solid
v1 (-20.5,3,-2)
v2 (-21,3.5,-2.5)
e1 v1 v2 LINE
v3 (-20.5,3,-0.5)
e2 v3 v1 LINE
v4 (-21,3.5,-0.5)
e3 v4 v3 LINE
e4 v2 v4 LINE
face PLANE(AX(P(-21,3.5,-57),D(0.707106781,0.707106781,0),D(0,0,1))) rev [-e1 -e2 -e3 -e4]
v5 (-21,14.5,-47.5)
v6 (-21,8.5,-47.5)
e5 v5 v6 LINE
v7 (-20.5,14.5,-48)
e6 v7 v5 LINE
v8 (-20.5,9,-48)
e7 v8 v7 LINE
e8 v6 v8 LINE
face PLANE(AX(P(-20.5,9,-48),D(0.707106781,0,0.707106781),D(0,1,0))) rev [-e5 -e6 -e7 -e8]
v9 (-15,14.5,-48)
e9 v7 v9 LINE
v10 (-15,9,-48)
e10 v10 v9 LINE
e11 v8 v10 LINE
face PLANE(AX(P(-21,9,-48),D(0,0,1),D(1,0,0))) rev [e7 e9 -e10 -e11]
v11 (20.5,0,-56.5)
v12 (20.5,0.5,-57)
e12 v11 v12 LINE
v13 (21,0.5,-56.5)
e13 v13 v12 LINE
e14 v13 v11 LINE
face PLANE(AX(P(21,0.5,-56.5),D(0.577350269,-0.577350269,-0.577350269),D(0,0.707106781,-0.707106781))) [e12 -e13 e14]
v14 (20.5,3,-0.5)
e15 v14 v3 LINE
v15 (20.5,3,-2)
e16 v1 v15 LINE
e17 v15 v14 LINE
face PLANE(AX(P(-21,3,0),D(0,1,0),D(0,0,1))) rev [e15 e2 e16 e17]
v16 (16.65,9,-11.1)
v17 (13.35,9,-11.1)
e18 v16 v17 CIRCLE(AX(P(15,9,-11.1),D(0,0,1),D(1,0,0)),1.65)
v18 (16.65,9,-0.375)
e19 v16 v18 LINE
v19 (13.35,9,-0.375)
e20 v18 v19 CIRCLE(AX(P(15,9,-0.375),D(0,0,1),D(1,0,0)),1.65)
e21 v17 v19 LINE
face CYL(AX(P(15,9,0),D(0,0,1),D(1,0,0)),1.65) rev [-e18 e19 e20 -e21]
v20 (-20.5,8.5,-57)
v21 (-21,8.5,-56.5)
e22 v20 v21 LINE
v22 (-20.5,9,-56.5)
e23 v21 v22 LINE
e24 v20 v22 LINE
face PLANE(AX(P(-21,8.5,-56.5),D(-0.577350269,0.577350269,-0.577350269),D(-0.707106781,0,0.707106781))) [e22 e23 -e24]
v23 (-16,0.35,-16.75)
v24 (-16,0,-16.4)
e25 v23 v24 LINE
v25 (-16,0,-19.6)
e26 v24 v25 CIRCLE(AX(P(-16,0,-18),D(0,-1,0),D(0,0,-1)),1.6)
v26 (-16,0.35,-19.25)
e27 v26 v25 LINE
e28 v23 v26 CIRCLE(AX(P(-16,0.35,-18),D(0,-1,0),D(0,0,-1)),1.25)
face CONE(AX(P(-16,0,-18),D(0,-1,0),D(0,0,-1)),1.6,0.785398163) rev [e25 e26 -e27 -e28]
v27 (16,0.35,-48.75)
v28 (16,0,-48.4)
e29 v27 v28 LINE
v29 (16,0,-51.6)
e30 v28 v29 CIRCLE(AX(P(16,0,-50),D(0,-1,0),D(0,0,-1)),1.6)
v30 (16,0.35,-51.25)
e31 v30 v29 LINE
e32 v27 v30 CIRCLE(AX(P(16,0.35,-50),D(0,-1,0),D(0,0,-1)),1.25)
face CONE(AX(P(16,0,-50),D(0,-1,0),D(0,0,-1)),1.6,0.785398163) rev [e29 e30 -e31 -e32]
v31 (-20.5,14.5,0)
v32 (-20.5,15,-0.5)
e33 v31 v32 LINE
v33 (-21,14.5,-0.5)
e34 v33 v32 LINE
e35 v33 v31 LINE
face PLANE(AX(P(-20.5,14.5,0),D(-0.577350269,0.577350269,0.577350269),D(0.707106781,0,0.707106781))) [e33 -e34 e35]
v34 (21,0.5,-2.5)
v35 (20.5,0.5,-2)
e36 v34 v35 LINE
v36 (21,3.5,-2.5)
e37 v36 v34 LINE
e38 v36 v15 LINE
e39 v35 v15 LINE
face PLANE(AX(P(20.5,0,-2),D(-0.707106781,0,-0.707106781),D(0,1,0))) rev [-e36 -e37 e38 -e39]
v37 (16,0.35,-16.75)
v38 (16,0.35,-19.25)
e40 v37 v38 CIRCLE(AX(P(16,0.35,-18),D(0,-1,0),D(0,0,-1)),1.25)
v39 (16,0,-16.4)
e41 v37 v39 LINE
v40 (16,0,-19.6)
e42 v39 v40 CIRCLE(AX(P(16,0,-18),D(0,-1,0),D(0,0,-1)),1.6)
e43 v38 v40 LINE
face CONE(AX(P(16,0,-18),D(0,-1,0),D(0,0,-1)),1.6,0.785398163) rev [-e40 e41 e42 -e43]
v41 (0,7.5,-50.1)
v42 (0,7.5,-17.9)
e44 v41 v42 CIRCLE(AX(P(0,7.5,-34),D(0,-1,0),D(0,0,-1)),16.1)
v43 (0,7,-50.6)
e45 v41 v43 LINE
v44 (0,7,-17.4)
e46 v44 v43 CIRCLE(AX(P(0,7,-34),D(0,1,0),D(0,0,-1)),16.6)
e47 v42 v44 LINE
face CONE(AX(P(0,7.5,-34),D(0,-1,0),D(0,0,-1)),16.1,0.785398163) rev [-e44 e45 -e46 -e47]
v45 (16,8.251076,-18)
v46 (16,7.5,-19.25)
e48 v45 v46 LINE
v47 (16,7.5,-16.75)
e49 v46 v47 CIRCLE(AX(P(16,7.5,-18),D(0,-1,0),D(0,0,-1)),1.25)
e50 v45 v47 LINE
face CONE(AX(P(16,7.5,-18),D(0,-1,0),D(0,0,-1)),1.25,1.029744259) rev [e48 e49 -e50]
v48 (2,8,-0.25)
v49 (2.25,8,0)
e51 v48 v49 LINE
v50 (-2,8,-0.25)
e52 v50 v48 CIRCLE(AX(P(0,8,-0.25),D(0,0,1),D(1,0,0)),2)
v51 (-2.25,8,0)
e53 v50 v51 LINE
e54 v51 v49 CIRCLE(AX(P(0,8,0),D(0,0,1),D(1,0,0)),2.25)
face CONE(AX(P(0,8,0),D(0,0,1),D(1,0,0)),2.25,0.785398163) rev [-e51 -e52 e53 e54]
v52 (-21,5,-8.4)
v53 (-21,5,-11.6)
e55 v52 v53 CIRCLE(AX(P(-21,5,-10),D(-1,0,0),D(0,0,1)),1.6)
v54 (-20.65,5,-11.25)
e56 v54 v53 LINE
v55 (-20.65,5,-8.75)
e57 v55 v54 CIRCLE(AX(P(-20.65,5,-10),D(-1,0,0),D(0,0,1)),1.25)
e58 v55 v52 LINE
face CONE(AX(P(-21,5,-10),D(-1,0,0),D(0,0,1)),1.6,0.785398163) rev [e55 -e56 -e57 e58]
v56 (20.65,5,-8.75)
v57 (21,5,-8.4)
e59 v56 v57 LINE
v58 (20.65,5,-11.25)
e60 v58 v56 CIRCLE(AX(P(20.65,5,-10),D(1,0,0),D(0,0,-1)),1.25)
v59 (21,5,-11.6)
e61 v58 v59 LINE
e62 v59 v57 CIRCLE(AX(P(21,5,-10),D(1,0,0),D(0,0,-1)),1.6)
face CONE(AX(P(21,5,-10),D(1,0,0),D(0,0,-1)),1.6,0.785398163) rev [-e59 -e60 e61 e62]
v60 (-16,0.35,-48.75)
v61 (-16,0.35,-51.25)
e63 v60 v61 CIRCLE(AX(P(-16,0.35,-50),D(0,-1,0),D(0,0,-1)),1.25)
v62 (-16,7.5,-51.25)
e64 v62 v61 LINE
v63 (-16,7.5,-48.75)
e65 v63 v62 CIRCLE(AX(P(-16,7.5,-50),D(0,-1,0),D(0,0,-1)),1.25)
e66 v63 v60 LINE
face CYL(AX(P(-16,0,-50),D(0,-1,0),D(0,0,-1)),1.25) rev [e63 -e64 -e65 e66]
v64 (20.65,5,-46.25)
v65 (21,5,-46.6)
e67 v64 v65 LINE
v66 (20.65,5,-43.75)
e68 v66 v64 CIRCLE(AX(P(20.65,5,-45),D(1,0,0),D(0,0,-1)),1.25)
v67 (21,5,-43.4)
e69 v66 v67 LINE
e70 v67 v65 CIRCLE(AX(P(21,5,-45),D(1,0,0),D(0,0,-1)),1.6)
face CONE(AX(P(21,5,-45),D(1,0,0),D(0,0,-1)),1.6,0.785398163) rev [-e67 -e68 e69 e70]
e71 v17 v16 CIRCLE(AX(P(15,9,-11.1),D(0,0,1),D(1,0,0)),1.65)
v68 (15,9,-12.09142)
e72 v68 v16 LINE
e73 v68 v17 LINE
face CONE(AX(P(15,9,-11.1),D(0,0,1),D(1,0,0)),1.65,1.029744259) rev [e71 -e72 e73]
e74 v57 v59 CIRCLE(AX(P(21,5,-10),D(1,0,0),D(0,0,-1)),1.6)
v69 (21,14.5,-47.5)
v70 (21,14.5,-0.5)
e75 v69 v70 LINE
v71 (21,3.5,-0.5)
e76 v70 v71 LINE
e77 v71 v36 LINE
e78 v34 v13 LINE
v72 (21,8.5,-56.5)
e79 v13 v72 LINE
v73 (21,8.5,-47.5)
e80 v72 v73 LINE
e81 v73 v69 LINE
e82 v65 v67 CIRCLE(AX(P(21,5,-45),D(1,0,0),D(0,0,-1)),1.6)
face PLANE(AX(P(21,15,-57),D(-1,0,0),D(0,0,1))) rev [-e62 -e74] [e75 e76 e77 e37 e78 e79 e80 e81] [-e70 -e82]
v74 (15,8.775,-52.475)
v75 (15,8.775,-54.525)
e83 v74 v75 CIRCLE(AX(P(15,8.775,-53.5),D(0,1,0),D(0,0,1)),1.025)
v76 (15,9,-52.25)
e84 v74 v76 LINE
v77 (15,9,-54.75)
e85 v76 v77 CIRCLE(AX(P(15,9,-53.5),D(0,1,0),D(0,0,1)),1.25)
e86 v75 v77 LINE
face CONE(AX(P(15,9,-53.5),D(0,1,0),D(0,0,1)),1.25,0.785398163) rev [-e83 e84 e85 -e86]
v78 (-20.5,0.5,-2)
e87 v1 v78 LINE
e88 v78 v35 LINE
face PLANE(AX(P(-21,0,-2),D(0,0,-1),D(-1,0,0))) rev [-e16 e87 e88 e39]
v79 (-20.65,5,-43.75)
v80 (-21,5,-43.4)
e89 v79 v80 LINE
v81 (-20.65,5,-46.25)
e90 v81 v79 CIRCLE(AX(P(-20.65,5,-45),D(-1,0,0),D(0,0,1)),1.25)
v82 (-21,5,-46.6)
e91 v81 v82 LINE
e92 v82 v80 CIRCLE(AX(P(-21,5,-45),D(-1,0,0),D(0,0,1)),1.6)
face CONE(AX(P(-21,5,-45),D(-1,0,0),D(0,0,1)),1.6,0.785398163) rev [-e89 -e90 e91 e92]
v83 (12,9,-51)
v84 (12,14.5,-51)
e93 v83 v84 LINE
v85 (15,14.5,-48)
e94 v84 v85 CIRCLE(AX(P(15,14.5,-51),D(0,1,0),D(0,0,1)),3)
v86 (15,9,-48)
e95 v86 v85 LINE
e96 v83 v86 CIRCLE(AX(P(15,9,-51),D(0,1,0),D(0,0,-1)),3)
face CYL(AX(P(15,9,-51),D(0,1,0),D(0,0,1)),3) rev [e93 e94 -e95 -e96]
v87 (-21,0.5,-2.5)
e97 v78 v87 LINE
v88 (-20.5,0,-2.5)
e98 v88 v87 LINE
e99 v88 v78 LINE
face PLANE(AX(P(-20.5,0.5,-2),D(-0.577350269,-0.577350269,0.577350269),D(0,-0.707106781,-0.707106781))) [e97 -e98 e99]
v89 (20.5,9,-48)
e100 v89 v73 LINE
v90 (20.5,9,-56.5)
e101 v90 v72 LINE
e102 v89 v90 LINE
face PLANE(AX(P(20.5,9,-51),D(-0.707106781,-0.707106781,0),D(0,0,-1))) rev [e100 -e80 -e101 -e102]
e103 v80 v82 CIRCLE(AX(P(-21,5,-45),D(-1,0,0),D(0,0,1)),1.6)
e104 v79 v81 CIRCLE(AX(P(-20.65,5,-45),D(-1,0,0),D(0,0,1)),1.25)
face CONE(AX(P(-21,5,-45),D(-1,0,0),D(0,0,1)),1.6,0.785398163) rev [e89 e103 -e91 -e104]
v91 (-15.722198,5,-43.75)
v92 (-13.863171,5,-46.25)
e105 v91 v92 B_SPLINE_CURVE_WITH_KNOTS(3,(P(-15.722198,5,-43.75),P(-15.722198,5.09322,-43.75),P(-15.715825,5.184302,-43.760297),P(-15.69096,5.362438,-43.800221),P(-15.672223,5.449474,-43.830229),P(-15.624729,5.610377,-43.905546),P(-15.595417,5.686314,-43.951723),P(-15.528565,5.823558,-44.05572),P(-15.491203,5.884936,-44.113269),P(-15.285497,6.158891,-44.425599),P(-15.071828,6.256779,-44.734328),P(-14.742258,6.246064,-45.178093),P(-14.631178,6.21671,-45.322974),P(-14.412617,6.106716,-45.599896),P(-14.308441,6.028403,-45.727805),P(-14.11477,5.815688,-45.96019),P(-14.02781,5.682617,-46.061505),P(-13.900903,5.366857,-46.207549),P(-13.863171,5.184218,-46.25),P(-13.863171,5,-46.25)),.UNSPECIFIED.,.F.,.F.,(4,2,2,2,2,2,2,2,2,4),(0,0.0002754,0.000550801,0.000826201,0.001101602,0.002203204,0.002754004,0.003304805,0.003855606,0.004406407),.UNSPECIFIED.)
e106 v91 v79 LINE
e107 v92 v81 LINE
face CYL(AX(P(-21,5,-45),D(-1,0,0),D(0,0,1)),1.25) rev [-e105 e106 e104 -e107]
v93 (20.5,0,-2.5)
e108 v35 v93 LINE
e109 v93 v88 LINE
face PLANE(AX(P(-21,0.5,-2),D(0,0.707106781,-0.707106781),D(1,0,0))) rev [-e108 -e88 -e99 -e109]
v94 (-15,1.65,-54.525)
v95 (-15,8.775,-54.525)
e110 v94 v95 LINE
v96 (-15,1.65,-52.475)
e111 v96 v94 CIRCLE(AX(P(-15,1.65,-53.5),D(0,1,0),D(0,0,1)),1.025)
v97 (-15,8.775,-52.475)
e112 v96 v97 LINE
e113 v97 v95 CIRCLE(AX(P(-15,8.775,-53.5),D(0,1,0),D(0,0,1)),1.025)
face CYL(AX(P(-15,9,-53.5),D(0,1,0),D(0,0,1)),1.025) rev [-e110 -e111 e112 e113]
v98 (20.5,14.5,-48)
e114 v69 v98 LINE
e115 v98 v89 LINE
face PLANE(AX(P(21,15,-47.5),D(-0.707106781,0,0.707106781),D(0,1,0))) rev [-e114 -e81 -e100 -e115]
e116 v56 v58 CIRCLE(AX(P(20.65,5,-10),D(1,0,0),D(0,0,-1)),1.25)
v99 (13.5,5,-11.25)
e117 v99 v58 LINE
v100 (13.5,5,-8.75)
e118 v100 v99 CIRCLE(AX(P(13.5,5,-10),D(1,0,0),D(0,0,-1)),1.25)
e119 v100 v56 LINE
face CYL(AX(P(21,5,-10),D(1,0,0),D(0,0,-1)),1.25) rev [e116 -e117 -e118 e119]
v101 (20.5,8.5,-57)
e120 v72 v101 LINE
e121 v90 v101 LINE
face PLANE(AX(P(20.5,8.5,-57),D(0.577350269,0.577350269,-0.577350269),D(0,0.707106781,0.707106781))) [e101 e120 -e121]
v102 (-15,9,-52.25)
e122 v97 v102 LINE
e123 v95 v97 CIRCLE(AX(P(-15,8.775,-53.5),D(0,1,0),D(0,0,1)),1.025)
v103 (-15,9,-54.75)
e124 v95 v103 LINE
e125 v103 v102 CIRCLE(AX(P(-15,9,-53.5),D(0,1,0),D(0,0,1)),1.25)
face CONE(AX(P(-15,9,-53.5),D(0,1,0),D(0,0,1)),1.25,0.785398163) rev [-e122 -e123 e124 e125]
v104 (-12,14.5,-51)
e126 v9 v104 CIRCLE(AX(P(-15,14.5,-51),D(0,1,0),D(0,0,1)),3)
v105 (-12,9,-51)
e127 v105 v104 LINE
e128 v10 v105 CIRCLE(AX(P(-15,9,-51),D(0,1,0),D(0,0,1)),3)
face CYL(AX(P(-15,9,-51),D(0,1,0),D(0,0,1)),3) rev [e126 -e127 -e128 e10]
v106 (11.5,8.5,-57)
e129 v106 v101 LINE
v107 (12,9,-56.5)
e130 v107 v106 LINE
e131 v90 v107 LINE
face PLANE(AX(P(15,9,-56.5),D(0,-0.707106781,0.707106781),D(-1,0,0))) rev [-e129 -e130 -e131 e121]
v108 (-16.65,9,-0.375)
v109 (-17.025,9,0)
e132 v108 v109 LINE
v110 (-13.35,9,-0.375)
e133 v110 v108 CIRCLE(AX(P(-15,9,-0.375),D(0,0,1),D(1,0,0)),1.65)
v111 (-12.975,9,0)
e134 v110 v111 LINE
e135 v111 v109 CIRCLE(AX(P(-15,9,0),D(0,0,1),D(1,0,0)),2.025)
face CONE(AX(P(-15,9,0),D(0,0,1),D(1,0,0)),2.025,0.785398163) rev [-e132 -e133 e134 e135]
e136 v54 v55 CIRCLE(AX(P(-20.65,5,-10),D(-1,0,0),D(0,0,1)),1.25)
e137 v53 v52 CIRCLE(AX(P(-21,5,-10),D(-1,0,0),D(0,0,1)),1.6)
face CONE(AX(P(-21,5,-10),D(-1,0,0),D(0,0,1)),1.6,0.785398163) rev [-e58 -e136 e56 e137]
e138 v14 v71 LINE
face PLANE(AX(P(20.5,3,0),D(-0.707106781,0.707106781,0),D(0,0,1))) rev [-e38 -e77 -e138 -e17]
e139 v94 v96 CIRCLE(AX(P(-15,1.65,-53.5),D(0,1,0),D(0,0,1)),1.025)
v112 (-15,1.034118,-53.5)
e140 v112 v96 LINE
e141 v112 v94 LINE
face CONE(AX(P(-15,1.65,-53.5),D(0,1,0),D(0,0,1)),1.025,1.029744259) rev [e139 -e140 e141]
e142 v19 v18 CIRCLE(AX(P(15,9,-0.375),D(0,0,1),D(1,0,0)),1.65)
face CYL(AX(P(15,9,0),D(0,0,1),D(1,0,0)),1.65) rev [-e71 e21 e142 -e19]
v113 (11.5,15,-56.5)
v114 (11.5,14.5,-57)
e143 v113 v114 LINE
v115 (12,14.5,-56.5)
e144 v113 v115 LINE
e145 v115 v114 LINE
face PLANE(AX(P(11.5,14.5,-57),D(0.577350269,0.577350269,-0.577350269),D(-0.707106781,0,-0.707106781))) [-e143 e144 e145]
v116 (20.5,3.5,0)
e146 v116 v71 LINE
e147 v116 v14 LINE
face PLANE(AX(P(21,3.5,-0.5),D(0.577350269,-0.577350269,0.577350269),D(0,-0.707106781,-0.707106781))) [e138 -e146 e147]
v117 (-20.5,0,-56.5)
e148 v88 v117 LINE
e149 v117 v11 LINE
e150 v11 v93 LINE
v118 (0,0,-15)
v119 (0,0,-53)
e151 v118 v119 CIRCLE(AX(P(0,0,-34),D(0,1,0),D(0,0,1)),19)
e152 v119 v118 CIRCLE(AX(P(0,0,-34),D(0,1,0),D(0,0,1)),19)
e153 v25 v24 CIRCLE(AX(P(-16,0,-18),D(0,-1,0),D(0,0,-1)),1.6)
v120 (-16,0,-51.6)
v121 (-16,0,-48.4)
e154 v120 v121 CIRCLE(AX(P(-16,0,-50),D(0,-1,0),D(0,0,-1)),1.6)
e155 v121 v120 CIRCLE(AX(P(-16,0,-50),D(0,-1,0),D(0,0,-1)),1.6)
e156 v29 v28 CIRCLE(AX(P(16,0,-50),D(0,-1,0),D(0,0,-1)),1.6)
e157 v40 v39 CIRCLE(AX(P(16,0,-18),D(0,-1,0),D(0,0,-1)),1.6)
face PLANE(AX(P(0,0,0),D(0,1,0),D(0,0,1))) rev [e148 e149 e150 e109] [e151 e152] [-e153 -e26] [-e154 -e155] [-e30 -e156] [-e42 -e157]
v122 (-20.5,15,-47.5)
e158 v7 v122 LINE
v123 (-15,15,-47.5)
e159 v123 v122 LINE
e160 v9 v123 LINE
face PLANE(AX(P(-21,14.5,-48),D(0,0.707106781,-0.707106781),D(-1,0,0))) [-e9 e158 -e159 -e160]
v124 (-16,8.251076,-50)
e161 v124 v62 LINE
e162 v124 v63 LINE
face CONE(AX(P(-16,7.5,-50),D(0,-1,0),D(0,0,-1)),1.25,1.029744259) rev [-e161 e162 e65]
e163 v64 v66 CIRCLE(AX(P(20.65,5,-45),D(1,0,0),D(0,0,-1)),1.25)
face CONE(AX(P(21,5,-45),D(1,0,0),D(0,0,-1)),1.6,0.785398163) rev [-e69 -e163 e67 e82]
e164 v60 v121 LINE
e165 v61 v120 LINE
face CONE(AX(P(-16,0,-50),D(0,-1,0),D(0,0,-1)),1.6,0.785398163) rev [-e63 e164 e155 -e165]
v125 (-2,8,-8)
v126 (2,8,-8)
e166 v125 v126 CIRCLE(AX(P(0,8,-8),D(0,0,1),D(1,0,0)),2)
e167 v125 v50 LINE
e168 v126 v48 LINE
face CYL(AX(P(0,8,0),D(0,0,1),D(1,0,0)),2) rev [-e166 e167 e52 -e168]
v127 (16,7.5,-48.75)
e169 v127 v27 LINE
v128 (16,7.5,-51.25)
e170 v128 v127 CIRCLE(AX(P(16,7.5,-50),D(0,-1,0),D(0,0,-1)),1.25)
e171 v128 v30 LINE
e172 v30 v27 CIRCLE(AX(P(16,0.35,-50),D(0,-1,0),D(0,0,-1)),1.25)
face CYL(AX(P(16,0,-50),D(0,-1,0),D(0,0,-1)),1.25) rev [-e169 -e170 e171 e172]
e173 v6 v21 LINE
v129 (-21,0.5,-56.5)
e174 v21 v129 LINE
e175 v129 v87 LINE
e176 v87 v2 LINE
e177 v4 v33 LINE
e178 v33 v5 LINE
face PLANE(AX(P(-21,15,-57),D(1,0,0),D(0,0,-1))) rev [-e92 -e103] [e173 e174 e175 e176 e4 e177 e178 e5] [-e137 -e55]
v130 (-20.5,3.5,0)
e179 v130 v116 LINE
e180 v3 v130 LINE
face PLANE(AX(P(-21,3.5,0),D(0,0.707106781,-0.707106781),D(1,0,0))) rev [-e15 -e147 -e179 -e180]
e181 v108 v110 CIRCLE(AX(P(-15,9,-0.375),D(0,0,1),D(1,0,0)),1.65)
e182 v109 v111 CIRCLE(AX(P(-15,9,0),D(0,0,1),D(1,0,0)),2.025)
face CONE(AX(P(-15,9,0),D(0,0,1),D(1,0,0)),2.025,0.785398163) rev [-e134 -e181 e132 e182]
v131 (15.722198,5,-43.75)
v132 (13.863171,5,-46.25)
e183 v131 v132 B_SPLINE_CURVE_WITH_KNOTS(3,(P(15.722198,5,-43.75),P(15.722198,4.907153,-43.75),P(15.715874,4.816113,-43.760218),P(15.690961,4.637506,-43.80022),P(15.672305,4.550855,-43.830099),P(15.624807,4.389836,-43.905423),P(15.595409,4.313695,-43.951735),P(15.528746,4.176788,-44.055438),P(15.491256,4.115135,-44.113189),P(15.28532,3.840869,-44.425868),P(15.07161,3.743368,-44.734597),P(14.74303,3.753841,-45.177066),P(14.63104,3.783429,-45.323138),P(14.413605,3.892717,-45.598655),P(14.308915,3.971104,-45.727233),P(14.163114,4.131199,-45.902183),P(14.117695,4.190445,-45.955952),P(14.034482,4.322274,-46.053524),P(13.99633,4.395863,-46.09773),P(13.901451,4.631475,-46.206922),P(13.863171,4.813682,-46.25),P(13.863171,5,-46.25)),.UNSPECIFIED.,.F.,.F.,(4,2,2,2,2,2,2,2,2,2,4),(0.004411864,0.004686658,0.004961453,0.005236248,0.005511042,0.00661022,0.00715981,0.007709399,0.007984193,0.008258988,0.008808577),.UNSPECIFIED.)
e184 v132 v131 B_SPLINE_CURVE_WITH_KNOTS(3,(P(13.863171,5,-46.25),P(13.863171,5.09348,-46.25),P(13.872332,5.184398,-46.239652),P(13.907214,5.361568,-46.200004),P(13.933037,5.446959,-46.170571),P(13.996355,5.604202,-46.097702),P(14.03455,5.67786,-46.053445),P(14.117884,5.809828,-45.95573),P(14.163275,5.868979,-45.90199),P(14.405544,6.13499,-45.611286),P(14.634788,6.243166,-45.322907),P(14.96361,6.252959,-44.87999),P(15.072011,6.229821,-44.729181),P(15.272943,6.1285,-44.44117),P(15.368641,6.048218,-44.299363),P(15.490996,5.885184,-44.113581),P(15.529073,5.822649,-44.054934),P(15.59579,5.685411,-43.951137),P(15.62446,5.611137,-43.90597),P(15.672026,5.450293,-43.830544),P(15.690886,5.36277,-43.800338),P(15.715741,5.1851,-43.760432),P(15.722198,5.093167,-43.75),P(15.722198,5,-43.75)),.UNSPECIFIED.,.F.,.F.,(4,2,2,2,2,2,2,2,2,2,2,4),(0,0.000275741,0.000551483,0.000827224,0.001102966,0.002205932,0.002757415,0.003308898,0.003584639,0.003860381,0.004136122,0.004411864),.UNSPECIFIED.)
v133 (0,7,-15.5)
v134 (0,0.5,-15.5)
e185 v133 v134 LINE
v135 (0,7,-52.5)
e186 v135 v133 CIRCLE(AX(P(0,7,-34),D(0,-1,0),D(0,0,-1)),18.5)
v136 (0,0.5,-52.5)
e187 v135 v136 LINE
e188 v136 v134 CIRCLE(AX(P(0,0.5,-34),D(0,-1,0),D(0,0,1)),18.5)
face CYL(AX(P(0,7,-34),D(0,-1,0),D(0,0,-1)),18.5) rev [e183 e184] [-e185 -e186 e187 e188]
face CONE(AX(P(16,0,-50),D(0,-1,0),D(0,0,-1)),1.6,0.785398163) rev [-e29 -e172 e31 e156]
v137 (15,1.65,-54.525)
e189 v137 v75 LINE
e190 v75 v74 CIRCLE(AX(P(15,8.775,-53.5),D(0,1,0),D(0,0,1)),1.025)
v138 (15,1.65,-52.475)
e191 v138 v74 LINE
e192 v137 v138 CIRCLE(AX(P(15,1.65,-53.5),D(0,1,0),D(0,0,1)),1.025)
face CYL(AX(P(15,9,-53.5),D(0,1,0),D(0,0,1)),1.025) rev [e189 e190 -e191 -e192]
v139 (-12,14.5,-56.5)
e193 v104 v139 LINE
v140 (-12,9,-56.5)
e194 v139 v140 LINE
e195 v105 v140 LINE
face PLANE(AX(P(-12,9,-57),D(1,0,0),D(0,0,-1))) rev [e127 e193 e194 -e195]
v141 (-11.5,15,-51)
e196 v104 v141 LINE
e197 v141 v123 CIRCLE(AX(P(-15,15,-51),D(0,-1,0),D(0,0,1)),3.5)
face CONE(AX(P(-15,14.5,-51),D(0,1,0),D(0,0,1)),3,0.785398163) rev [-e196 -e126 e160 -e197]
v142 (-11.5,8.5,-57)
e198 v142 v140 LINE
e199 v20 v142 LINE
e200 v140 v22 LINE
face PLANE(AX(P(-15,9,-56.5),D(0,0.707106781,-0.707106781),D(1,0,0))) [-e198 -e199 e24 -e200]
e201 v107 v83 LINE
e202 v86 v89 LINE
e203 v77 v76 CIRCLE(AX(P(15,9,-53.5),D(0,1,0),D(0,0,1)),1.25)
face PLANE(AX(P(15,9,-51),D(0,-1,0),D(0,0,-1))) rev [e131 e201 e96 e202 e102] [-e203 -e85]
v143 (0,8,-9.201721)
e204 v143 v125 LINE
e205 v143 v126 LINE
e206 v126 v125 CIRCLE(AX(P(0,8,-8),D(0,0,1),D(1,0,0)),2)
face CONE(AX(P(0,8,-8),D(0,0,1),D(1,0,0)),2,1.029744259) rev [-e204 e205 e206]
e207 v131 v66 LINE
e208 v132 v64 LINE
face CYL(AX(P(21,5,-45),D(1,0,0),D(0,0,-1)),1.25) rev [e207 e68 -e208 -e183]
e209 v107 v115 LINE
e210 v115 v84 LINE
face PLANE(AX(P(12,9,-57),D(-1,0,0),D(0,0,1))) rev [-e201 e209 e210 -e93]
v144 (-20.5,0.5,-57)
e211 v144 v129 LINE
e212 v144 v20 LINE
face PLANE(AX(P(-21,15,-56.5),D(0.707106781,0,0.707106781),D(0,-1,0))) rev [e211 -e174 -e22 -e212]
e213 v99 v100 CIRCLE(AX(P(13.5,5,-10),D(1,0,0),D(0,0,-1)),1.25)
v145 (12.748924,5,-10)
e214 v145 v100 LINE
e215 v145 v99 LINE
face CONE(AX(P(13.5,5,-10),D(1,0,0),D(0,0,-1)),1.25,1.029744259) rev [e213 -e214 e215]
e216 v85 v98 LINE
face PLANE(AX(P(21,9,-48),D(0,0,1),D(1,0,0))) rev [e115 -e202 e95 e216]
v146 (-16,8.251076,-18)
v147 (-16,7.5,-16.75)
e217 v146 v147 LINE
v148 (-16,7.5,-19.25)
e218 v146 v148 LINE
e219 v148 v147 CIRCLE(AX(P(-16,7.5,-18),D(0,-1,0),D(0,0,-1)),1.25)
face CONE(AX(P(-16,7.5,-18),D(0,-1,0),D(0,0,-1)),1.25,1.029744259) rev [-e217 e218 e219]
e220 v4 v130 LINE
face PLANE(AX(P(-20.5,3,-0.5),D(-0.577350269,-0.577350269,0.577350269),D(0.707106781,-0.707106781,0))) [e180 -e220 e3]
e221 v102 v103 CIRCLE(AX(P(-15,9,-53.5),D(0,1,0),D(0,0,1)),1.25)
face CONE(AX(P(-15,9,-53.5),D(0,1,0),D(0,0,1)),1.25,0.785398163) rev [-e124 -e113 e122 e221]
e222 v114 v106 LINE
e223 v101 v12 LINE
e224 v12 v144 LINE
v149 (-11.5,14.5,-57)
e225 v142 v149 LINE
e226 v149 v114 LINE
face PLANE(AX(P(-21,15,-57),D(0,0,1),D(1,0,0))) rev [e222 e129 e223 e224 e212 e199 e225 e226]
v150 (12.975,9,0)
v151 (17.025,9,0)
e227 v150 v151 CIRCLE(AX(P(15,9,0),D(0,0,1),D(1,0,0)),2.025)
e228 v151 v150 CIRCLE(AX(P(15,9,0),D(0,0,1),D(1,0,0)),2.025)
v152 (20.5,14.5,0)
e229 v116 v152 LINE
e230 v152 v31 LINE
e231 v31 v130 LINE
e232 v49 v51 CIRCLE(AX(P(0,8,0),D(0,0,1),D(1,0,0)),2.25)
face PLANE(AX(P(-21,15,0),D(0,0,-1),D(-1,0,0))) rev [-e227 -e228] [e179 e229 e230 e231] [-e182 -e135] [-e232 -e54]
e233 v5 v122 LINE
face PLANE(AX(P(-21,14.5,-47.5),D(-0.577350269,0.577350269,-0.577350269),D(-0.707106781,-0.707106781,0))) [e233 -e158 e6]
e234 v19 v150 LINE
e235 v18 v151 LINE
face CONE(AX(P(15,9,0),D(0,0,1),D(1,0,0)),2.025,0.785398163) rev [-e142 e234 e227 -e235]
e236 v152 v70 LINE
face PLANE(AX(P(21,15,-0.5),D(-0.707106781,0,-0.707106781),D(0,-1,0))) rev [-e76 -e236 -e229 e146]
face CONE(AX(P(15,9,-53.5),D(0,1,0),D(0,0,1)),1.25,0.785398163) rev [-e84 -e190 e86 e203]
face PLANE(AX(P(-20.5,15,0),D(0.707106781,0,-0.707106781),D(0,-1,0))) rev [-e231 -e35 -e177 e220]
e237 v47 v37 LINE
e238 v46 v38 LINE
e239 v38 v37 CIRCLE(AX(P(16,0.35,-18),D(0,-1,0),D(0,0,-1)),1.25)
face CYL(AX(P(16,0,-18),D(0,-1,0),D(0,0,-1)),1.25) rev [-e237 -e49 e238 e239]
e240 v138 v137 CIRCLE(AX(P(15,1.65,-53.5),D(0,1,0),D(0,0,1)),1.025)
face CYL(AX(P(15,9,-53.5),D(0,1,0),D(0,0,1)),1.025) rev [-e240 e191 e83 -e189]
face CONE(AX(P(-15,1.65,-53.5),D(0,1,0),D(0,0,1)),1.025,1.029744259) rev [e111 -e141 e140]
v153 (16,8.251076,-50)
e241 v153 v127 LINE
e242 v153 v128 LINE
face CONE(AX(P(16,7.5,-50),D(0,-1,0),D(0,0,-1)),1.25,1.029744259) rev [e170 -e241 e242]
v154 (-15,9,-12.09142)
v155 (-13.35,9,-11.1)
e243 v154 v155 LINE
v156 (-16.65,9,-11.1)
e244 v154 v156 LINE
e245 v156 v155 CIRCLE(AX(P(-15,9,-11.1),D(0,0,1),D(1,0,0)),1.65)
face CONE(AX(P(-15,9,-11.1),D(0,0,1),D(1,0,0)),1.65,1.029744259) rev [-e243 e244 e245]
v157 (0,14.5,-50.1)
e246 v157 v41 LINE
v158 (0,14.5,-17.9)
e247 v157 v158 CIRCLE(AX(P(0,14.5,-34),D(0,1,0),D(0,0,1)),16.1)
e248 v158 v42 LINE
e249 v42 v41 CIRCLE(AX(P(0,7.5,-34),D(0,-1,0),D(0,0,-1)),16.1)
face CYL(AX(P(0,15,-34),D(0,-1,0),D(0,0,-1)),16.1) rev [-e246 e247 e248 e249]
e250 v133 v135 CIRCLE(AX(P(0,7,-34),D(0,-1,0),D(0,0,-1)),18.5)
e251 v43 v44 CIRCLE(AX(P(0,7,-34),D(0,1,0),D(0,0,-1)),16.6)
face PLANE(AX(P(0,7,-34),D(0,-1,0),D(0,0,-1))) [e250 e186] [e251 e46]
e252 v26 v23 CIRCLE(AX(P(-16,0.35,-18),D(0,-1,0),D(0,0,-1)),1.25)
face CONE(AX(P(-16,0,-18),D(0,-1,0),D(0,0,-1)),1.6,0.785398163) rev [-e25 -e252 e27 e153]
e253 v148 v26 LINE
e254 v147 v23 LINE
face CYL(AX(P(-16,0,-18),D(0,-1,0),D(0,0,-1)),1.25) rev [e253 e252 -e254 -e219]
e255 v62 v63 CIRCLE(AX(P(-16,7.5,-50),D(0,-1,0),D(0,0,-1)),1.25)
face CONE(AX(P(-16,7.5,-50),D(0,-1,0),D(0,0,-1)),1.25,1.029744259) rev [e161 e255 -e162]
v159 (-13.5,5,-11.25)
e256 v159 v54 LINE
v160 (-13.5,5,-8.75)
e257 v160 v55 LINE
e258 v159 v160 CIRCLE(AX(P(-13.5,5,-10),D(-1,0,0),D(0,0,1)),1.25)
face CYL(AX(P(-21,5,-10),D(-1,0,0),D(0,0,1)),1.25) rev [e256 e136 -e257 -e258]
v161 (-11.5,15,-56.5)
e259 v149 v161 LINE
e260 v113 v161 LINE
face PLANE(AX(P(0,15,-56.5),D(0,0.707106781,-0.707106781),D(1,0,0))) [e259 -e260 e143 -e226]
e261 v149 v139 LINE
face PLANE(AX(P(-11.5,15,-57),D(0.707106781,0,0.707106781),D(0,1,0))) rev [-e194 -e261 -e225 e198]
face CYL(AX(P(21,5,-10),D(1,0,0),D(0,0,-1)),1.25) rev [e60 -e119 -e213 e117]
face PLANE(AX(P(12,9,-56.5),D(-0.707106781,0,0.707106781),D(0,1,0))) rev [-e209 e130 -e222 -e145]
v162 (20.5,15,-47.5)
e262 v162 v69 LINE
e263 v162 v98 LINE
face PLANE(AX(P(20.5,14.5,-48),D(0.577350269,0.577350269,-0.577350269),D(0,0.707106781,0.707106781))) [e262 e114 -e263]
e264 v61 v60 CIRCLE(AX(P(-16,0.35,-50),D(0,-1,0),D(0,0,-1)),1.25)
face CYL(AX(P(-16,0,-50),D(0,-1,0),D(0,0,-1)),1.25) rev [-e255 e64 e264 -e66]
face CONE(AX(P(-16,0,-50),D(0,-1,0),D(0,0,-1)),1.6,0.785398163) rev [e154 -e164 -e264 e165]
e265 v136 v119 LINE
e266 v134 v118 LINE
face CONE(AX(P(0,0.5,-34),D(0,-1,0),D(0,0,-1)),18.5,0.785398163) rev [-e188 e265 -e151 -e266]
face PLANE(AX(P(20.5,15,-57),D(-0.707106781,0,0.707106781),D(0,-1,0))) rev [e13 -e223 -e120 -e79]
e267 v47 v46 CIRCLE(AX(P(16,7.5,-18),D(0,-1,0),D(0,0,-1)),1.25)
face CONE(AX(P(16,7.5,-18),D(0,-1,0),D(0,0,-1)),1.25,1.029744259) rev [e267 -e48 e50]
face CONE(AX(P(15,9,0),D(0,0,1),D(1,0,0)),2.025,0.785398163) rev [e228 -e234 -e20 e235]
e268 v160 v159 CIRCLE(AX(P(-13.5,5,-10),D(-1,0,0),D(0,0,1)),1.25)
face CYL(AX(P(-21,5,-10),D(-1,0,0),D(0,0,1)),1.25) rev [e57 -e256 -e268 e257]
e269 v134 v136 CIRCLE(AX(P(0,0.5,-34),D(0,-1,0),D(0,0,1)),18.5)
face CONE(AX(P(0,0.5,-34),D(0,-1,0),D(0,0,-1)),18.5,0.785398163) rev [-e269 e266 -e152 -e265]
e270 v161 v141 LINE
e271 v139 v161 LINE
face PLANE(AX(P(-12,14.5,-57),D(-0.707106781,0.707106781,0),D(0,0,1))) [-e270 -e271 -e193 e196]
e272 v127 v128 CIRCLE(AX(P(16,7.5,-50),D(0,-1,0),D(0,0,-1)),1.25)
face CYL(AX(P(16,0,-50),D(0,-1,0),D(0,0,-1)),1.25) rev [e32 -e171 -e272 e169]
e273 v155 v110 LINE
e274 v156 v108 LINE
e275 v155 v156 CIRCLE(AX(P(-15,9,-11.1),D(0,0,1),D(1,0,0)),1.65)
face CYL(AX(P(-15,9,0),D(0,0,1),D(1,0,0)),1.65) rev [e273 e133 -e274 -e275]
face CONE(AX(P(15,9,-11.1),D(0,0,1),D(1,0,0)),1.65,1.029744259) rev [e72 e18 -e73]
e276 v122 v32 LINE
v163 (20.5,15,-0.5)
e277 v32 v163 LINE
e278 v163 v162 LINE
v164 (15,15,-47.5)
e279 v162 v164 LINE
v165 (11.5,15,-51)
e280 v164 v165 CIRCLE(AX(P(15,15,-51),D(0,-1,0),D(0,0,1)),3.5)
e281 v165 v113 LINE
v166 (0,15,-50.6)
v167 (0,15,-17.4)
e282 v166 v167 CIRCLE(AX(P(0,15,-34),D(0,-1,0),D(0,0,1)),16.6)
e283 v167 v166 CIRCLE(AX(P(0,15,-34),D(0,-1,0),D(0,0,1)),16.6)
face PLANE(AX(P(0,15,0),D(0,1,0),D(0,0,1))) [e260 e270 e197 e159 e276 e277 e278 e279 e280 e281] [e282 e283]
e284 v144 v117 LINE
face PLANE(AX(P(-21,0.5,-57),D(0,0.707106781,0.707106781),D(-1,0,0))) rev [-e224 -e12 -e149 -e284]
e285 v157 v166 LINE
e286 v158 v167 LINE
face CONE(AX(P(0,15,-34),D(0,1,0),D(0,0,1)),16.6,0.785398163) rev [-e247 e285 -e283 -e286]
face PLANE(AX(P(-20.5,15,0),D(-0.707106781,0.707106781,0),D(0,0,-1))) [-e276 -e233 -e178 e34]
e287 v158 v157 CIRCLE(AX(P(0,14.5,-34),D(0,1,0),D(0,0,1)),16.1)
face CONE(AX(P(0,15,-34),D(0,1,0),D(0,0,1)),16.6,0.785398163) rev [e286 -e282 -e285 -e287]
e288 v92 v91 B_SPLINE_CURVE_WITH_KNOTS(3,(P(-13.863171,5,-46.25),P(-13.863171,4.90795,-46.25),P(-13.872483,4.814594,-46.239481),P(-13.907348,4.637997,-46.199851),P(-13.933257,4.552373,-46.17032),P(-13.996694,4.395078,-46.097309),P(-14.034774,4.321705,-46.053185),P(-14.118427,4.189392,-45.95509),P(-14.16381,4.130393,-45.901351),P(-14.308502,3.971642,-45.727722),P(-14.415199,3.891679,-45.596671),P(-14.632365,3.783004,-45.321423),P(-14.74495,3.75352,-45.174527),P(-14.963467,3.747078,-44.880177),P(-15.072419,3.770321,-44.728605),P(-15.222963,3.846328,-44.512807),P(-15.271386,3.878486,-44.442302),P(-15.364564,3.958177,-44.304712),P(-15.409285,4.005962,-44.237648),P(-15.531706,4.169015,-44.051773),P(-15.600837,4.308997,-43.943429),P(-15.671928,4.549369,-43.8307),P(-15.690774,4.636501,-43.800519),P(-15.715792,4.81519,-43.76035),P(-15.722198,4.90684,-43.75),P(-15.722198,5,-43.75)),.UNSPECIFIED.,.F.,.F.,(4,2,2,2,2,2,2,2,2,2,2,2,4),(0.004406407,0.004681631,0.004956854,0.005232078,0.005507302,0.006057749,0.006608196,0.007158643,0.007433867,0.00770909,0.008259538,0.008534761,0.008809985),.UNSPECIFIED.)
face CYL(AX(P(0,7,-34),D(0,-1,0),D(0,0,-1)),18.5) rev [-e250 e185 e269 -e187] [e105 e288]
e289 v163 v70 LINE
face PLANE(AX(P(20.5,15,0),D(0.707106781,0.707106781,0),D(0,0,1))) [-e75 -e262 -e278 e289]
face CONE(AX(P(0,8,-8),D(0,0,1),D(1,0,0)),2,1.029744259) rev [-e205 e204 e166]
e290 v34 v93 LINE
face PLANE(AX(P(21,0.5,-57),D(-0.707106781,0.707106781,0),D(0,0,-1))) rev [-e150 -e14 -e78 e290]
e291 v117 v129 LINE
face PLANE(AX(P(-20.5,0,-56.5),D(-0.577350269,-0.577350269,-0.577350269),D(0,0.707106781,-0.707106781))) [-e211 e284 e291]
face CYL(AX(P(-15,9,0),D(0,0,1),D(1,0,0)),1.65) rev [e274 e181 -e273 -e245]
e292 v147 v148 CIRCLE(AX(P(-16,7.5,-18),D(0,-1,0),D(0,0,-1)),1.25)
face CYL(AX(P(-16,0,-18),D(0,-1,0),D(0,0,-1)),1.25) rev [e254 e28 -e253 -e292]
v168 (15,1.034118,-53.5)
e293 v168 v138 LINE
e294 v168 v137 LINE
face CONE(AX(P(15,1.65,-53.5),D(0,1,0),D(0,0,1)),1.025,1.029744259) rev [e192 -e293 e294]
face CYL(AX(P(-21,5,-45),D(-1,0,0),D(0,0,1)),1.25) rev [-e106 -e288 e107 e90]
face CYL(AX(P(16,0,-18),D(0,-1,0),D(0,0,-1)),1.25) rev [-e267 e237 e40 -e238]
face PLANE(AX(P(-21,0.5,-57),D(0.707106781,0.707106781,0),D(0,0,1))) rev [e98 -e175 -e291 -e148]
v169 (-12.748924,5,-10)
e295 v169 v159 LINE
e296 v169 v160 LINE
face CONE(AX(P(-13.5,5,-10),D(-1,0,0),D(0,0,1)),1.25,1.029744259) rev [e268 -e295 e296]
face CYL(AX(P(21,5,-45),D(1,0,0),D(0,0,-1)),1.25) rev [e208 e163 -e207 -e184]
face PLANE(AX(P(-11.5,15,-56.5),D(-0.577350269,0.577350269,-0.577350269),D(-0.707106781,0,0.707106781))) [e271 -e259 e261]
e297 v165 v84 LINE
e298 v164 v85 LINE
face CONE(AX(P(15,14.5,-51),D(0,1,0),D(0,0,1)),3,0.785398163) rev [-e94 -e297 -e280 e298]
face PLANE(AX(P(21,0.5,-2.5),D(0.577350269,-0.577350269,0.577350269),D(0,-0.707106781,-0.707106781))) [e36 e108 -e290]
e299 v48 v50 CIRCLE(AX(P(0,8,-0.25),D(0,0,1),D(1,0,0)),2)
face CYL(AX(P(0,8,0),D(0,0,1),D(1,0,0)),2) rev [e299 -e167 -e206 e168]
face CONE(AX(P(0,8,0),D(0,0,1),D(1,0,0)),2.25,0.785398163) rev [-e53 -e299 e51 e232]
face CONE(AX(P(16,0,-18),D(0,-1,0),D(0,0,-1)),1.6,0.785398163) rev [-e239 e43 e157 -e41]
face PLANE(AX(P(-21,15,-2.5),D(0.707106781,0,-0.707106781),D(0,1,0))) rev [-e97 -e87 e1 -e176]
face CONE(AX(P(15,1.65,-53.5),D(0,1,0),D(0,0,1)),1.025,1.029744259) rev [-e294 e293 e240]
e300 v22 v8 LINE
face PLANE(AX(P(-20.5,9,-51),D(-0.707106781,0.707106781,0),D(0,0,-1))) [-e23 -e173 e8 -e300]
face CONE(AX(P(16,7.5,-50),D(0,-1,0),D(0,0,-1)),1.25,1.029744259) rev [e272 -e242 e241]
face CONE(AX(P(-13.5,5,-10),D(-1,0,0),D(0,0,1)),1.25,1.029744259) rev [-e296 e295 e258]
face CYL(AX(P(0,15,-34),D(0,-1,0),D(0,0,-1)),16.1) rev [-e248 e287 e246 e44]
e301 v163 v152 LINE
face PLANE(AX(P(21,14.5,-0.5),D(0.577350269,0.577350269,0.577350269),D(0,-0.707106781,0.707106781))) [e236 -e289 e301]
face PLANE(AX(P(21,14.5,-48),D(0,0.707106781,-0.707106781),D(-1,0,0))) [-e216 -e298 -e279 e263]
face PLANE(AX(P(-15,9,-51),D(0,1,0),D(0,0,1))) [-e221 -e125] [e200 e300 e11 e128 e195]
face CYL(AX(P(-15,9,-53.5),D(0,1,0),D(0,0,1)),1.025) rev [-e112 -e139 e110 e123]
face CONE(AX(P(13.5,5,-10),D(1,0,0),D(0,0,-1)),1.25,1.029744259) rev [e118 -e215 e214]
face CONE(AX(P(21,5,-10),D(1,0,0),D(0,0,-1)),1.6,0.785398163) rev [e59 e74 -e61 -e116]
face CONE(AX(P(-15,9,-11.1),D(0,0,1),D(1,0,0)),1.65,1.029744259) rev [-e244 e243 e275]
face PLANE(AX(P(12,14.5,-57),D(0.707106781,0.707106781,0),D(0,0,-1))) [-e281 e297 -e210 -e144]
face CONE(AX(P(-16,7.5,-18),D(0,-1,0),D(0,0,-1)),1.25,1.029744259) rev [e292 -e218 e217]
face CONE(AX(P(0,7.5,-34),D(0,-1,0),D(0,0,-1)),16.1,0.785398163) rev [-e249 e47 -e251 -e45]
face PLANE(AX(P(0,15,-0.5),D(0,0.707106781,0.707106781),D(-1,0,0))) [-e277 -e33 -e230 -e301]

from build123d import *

# Parameters (mm, degrees)
SKETCH1_W                       = 42
SKETCH1_H                       = 57
BOSS_EXTRUDE1_DEPTH             = 15
SKETCH2_R                       = 18.5
CUT_EXTRUDE1_DEPTH              = 7
SKETCH3_R                       = 16.1
CUT_EXTRUDE2_DEPTH              = 62.269894728
SKETCH4_W                       = 2
SKETCH4_H                       = 3
CUT_EXTRUDE3_DEPTH              = 73.374028491
M4_TAPPED_HOLE1_D               = 3.3
M4_TAPPED_HOLE1_DEPTH           = 11.1
M4_TAPPED_HOLE1_CSINK_D         = 4.05
M4_TAPPED_HOLE1_CSINK_ANGLE     = 90
M4_TAPPED_HOLE1_TIP             = 0.991420021
SIZE_MM_DOWEL_HOLE1_D           = 4
SIZE_MM_DOWEL_HOLE1_DEPTH       = 8
SIZE_MM_DOWEL_HOLE1_CSINK_D     = 4.5
SIZE_MM_DOWEL_HOLE1_CSINK_ANGLE = 90
SIZE_MM_DOWEL_HOLE1_TIP         = 1.201721238
M3_TAPPED_HOLE1_D               = 2.5
M3_TAPPED_HOLE1_DEPTH           = 7.5
M3_TAPPED_HOLE1_CSINK_D         = 3.2
M3_TAPPED_HOLE1_CSINK_ANGLE     = 90
M3_TAPPED_HOLE1_TIP             = 0.751075774
CUT_EXTRUDE4_DEPTH              = 6
M2_5_TAPPED_HOLE1_D             = 2.05
M2_5_TAPPED_HOLE1_DEPTH         = 7.35
M2_5_TAPPED_HOLE1_CSINK_D       = 2.5
M2_5_TAPPED_HOLE1_CSINK_ANGLE   = 90
M2_5_TAPPED_HOLE1_TIP           = 0.615882135
M3_TAPPED_HOLE3_D               = 2.5
M3_TAPPED_HOLE3_DEPTH           = 7.5
M3_TAPPED_HOLE3_CSINK_D         = 3.2
M3_TAPPED_HOLE3_CSINK_ANGLE     = 90
M3_TAPPED_HOLE3_TIP             = 0.751075774
M3_TAPPED_HOLE4_D               = 2.5
M3_TAPPED_HOLE4_DEPTH           = 7.5
M3_TAPPED_HOLE4_CSINK_D         = 3.2
M3_TAPPED_HOLE4_CSINK_ANGLE     = 90
M3_TAPPED_HOLE4_TIP             = 0.751075774
CHAMFER1_SIZE                   = 0.5


with BuildPart() as part:
    # Sketch1 → Boss-Extrude1 (new body)
    with BuildSketch(Plane(origin=(0, 0, 0), x_dir=(1, 0, 0), z_dir=(0, 1, 0))):
        with Locations((0, 28.5)):
            Rectangle(SKETCH1_W, SKETCH1_H)
    extrude(amount=BOSS_EXTRUDE1_DEPTH)

    # Sketch2 → Cut-Extrude1 (cut)
    with BuildSketch(Plane.XZ):
        with Locations(Location((0, -34, 0), (0, 0, 270))):
            Circle(SKETCH2_R)
    extrude(amount=-CUT_EXTRUDE1_DEPTH, mode=Mode.SUBTRACT)

    # Sketch3 → Cut-Extrude2 (cut, through all)
    with BuildSketch(Plane.XZ.offset(-7)):
        with Locations(Location((0, -34, 0), (0, 0, 270))):
            Circle(SKETCH3_R)
    extrude(amount=-CUT_EXTRUDE2_DEPTH, mode=Mode.SUBTRACT)

    # Sketch4 → Cut-Extrude3 (cut, through all)
    with BuildSketch(Plane(origin=(21, 0, 0), x_dir=(0, 0, -1), z_dir=(1, 0, 0))):
        with Locations((1, 1.5)):
            Rectangle(SKETCH4_W, SKETCH4_H)
    extrude(amount=-CUT_EXTRUDE3_DEPTH, mode=Mode.SUBTRACT)

    # M4 Tapped Hole1
    with Locations(Plane.XY):
        with Locations((-15, 9), (15, 9)):
            CounterSinkHole(M4_TAPPED_HOLE1_D / 2, M4_TAPPED_HOLE1_CSINK_D / 2, depth=M4_TAPPED_HOLE1_DEPTH, counter_sink_angle=M4_TAPPED_HOLE1_CSINK_ANGLE)
            with Locations((0, 0, -(M4_TAPPED_HOLE1_DEPTH + M4_TAPPED_HOLE1_TIP / 2))):  # 118° drill point
                Cone(0, M4_TAPPED_HOLE1_D / 2, M4_TAPPED_HOLE1_TIP, mode=Mode.SUBTRACT)

    # Size mm Dowel Hole1
    with Locations(Plane.XY):
        with Locations((0, 8)):
            CounterSinkHole(SIZE_MM_DOWEL_HOLE1_D / 2, SIZE_MM_DOWEL_HOLE1_CSINK_D / 2, depth=SIZE_MM_DOWEL_HOLE1_DEPTH, counter_sink_angle=SIZE_MM_DOWEL_HOLE1_CSINK_ANGLE)
            with Locations((0, 0, -(SIZE_MM_DOWEL_HOLE1_DEPTH + SIZE_MM_DOWEL_HOLE1_TIP / 2))):  # 118° drill point
                Cone(0, SIZE_MM_DOWEL_HOLE1_D / 2, SIZE_MM_DOWEL_HOLE1_TIP, mode=Mode.SUBTRACT)

    # M3 Tapped Hole1
    with Locations(Plane(origin=(0, 0, 0), x_dir=(-1, 0, 0), z_dir=(0, -1, 0))):
        with Locations((16, 18), (-16, 18), (-16, 50), (16, 50)):
            CounterSinkHole(M3_TAPPED_HOLE1_D / 2, M3_TAPPED_HOLE1_CSINK_D / 2, depth=M3_TAPPED_HOLE1_DEPTH, counter_sink_angle=M3_TAPPED_HOLE1_CSINK_ANGLE)
            with Locations((0, 0, -(M3_TAPPED_HOLE1_DEPTH + M3_TAPPED_HOLE1_TIP / 2))):  # 118° drill point
                Cone(0, M3_TAPPED_HOLE1_D / 2, M3_TAPPED_HOLE1_TIP, mode=Mode.SUBTRACT)

    # Sketch12 → Cut-Extrude4 (cut)
    with BuildSketch(Plane(origin=(0, 15, 0), x_dir=(1, 0, 0), z_dir=(0, 1, 0))):
        with BuildLine():
            Line((-21, 57), (-12, 57))
            Line((-12, 57), (-12, 51))
            ThreePointArc((-12, 51), (-12.878679656, 48.878679656), (-15, 48))
            Line((-15, 48), (-21, 48))
            Line((-21, 48), (-21, 57))
        make_face()
        with BuildLine():
            Line((12, 57), (12, 51))
            ThreePointArc((12, 51), (12.878679656, 48.878679656), (15, 48))
            Line((15, 48), (21, 48))
            Line((21, 48), (21, 57))
            Line((21, 57), (12, 57))
        make_face()
    extrude(amount=-CUT_EXTRUDE4_DEPTH, mode=Mode.SUBTRACT)

    # M2.5 Tapped Hole1
    with Locations(Plane(origin=(0, 9, 0), x_dir=(1, 0, 0), z_dir=(0, 1, 0))):
        with Locations((-15, 53.5), (15, 53.5)):
            CounterSinkHole(M2_5_TAPPED_HOLE1_D / 2, M2_5_TAPPED_HOLE1_CSINK_D / 2, depth=M2_5_TAPPED_HOLE1_DEPTH, counter_sink_angle=M2_5_TAPPED_HOLE1_CSINK_ANGLE)
            with Locations((0, 0, -(M2_5_TAPPED_HOLE1_DEPTH + M2_5_TAPPED_HOLE1_TIP / 2))):  # 118° drill point
                Cone(0, M2_5_TAPPED_HOLE1_D / 2, M2_5_TAPPED_HOLE1_TIP, mode=Mode.SUBTRACT)

    # M3 Tapped Hole3
    with Locations(Plane.ZY.offset(21)):
        with Locations((-45, 5), (-10, 5)):
            CounterSinkHole(M3_TAPPED_HOLE3_D / 2, M3_TAPPED_HOLE3_CSINK_D / 2, depth=M3_TAPPED_HOLE3_DEPTH, counter_sink_angle=M3_TAPPED_HOLE3_CSINK_ANGLE)
            with Locations((0, 0, -(M3_TAPPED_HOLE3_DEPTH + M3_TAPPED_HOLE3_TIP / 2))):  # 118° drill point
                Cone(0, M3_TAPPED_HOLE3_D / 2, M3_TAPPED_HOLE3_TIP, mode=Mode.SUBTRACT)

    # M3 Tapped Hole4
    with Locations(Plane(origin=(21, 0, 0), x_dir=(0, 0, -1), z_dir=(1, 0, 0))):
        with Locations((10, 5), (45, 5)):
            CounterSinkHole(M3_TAPPED_HOLE4_D / 2, M3_TAPPED_HOLE4_CSINK_D / 2, depth=M3_TAPPED_HOLE4_DEPTH, counter_sink_angle=M3_TAPPED_HOLE4_CSINK_ANGLE)
            with Locations((0, 0, -(M3_TAPPED_HOLE4_DEPTH + M3_TAPPED_HOLE4_TIP / 2))):  # 118° drill point
                Cone(0, M3_TAPPED_HOLE4_D / 2, M3_TAPPED_HOLE4_TIP, mode=Mode.SUBTRACT)

    # Chamfer1
    chamfer1_edges = [part.edges().sort_by_distance(p)[0] for p in [
        (-21, 9, -52.5),
        (-21, 12, -48),
        (-16.5, 9, -57),
        (-12, 12, -57),
        (-18, 15, -48),
        (-12.878679656, 15, -48.878679656),
        (-12, 15, -54),
        (16.5, 9, -57),
        (12, 12, -57),
        (21, 9, -52.5),
        (21, 12, -48),
        (12.878679656, 15, -48.878679656),
        (18, 15, -48),
        (12, 15, -54),
        (21, 15, -24),
        (0, 0, -15.5),
        (0, 15, -17.9),
        (0, 7, -17.9),
        (21, 0, -29.5),
        (-21, 3, -1),
        (0, 3, 0),
        (-21, 1.5, -2),
        (0, 0, -2),
        (21, 1.5, -2),
        (21, 3, -1),
        (0, 0, -57),
        (-21, 0, -29.5),
        (21, 9, 0),
        (-21, 9, 0),
        (0, 15, 0),
        (-21, 15, -24),
        (0, 15, -57),
        (-21, 4.5, -57),
        (21, 4.5, -57),
    ]]
    chamfer(chamfer1_edges, length=CHAMFER1_SIZE)


solid = part.part
